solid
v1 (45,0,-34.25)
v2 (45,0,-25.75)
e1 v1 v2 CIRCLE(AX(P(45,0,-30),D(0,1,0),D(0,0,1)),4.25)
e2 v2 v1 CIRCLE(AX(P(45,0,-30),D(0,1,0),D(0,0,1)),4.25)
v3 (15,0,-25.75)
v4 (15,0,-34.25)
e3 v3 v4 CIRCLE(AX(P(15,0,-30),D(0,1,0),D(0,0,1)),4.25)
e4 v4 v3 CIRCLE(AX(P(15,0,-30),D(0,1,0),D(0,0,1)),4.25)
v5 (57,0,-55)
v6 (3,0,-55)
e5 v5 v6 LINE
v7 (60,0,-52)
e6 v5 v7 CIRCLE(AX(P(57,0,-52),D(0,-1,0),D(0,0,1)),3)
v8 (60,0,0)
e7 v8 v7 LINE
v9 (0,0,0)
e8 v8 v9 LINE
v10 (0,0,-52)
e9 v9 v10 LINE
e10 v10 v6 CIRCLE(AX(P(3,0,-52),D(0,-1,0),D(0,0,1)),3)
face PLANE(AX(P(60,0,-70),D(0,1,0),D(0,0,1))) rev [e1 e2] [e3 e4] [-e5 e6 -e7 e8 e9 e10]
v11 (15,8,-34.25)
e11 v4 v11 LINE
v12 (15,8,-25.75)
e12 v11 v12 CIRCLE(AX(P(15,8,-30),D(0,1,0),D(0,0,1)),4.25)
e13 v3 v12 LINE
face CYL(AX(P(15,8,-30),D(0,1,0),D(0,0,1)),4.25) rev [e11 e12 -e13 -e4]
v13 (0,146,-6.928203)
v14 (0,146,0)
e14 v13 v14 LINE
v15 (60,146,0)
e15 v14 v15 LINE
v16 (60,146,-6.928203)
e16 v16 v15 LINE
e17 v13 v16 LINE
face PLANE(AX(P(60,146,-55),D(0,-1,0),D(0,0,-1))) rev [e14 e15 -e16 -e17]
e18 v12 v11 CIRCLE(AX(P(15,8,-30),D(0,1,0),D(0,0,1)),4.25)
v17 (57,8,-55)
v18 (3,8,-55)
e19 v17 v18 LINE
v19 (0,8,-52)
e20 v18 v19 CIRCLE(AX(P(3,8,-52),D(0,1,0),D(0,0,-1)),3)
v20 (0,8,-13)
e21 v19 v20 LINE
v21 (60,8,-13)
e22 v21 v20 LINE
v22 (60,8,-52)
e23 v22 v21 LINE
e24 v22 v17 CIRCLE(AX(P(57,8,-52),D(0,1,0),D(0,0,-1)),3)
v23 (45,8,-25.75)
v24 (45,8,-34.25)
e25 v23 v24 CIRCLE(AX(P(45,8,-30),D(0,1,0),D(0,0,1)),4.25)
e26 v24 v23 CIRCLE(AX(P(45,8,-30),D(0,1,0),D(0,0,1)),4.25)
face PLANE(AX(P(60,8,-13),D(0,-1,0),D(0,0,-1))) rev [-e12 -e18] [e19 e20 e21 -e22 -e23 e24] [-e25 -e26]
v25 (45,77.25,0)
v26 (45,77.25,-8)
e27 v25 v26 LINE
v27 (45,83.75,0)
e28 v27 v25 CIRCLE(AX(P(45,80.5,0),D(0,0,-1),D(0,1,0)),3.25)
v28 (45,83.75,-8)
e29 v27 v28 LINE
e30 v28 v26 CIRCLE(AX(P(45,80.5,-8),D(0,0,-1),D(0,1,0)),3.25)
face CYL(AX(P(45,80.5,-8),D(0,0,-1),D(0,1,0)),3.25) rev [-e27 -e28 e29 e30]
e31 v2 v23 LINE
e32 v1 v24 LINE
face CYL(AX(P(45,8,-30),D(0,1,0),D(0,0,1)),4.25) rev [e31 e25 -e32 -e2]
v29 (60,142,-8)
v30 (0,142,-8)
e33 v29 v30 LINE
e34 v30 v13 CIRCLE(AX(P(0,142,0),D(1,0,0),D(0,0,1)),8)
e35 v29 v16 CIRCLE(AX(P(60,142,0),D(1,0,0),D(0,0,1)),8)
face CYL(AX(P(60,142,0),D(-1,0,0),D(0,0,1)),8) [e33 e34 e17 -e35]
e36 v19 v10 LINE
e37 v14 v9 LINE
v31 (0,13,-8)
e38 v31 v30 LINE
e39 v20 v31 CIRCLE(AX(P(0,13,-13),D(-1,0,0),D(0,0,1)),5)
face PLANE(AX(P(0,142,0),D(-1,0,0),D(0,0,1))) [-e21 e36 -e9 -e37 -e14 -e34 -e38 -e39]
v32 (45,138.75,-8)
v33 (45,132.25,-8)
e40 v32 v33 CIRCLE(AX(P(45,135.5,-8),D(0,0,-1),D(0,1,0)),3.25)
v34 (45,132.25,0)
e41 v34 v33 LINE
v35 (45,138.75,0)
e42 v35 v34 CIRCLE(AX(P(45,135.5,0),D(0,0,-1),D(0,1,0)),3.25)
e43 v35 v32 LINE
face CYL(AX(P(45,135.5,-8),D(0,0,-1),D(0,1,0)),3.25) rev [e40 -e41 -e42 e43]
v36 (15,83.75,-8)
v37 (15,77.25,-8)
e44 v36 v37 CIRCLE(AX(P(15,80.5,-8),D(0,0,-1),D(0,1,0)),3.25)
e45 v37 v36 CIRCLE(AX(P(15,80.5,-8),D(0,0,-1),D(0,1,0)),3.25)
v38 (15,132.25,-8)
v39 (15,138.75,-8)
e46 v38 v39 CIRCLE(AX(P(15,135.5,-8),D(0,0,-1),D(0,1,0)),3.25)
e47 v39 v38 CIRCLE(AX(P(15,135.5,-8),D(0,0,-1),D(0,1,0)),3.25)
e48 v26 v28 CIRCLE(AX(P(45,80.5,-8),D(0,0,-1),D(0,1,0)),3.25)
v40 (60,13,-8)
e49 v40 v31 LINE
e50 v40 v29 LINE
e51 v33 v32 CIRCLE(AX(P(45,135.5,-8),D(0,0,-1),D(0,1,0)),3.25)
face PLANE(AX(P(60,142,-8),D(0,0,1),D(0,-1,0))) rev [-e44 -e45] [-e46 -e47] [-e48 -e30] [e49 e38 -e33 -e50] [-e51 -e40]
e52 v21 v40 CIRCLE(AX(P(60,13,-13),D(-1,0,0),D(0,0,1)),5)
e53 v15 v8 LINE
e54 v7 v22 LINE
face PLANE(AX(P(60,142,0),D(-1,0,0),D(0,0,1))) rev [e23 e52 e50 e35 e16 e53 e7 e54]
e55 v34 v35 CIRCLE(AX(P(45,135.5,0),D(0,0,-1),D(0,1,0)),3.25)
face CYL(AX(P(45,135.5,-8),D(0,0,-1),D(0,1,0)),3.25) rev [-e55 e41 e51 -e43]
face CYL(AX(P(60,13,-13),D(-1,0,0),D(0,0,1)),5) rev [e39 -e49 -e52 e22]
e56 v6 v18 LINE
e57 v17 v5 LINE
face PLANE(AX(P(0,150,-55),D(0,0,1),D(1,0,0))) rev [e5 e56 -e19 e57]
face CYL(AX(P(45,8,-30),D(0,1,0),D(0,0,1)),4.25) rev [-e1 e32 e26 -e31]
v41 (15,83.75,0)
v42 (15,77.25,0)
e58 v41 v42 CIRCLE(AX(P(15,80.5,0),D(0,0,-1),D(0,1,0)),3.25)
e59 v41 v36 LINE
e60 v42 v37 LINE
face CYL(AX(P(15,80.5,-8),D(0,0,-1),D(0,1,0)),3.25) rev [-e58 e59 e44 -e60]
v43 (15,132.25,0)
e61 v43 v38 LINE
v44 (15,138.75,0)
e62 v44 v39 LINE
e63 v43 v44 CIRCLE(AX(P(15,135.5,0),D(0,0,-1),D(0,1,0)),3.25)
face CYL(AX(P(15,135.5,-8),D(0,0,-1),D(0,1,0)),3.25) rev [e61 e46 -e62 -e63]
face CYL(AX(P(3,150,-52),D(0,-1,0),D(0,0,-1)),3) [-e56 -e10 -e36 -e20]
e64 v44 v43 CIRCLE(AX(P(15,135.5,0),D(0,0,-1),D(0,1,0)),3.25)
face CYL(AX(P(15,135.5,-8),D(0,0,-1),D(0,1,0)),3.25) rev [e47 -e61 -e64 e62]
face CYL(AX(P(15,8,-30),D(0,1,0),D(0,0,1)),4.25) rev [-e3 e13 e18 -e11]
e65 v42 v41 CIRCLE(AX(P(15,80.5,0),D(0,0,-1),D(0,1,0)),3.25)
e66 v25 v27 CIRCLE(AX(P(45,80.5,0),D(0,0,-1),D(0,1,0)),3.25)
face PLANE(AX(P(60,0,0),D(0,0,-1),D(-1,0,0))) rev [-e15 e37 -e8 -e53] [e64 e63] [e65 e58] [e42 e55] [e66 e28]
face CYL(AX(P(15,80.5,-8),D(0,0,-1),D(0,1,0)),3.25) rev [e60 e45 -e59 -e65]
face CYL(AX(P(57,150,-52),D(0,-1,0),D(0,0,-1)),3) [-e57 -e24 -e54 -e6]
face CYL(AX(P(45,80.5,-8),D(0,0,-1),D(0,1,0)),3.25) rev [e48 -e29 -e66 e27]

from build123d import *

# Parameters (mm, degrees)
MEMBER_1_DEPTH          = 60
SKETCH_3_W              = 60
SKETCH_3_H              = 15
CUT_EXTRUDE_1_DEPTH     = 177.068168617
SKETCH_4_W              = 60
SKETCH_4_H              = 4
CUT_EXTRUDE_2_DEPTH     = 171.660481659
HOLE_WIZARD_6_5_6_5_1_D = 6.5
FILLET_1_R              = 3
HOLE_WIZARD_8_5_8_5_1_D = 8.5


with BuildPart() as part:
    # Sketch1 → Member 1 (new body)
    with BuildSketch(Plane(origin=(0, 0, 0), x_dir=(0, 0, -1), z_dir=(1, 0, 0))):
        with BuildLine():
            Line((0, 0), (0, 150))
            ThreePointArc((0, 150), (5.656854249, 147.656854249), (8, 142))
            Line((8, 142), (8, 13))
            ThreePointArc((8, 13), (9.464466094, 9.464466094), (13, 8))
            Line((13, 8), (62, 8))
            ThreePointArc((62, 8), (67.656854249, 5.656854249), (70, 0))
            Line((70, 0), (0, 0))
        make_face()
    extrude(amount=MEMBER_1_DEPTH)

    # 草图3 → 切除-拉伸1 (cut, through all)
    with BuildSketch(Plane.XZ):
        with Locations((30, -62.5)):
            Rectangle(SKETCH_3_W, SKETCH_3_H)
    extrude(amount=-CUT_EXTRUDE_1_DEPTH, mode=Mode.SUBTRACT)

    # 草图4 → 切除-拉伸2 (cut, through all)
    with BuildSketch(Plane.XY):
        with Locations((30, 148)):
            Rectangle(SKETCH_4_W, SKETCH_4_H)
    extrude(amount=-CUT_EXTRUDE_2_DEPTH, mode=Mode.SUBTRACT)

    # Ø6.5 (6.5) 直径孔1 (through all)
    with Locations(Plane(origin=(0, 0, -8), x_dir=(-1, 0, 0), z_dir=(0, 0, -1))):
        with Locations((-45, 135.5), (-15, 135.5), (-45, 80.5), (-15, 80.5)):
            Hole(HOLE_WIZARD_6_5_6_5_1_D / 2)

    # 圆角1
    fillet_1_edges = [part.edges().sort_by_distance(p)[0] for p in [
        (0, 4, -55),
        (60, 4, -55),
    ]]
    fillet(fillet_1_edges, radius=FILLET_1_R)

    # Ø8.5 (8.5) 直径孔1 (through all)
    with Locations(Plane(origin=(0, 8, 0), x_dir=(1, 0, 0), z_dir=(0, 1, 0))):
        with Locations((15, 30), (45, 30)):
            Hole(HOLE_WIZARD_8_5_8_5_1_D / 2)


solid = part.part
